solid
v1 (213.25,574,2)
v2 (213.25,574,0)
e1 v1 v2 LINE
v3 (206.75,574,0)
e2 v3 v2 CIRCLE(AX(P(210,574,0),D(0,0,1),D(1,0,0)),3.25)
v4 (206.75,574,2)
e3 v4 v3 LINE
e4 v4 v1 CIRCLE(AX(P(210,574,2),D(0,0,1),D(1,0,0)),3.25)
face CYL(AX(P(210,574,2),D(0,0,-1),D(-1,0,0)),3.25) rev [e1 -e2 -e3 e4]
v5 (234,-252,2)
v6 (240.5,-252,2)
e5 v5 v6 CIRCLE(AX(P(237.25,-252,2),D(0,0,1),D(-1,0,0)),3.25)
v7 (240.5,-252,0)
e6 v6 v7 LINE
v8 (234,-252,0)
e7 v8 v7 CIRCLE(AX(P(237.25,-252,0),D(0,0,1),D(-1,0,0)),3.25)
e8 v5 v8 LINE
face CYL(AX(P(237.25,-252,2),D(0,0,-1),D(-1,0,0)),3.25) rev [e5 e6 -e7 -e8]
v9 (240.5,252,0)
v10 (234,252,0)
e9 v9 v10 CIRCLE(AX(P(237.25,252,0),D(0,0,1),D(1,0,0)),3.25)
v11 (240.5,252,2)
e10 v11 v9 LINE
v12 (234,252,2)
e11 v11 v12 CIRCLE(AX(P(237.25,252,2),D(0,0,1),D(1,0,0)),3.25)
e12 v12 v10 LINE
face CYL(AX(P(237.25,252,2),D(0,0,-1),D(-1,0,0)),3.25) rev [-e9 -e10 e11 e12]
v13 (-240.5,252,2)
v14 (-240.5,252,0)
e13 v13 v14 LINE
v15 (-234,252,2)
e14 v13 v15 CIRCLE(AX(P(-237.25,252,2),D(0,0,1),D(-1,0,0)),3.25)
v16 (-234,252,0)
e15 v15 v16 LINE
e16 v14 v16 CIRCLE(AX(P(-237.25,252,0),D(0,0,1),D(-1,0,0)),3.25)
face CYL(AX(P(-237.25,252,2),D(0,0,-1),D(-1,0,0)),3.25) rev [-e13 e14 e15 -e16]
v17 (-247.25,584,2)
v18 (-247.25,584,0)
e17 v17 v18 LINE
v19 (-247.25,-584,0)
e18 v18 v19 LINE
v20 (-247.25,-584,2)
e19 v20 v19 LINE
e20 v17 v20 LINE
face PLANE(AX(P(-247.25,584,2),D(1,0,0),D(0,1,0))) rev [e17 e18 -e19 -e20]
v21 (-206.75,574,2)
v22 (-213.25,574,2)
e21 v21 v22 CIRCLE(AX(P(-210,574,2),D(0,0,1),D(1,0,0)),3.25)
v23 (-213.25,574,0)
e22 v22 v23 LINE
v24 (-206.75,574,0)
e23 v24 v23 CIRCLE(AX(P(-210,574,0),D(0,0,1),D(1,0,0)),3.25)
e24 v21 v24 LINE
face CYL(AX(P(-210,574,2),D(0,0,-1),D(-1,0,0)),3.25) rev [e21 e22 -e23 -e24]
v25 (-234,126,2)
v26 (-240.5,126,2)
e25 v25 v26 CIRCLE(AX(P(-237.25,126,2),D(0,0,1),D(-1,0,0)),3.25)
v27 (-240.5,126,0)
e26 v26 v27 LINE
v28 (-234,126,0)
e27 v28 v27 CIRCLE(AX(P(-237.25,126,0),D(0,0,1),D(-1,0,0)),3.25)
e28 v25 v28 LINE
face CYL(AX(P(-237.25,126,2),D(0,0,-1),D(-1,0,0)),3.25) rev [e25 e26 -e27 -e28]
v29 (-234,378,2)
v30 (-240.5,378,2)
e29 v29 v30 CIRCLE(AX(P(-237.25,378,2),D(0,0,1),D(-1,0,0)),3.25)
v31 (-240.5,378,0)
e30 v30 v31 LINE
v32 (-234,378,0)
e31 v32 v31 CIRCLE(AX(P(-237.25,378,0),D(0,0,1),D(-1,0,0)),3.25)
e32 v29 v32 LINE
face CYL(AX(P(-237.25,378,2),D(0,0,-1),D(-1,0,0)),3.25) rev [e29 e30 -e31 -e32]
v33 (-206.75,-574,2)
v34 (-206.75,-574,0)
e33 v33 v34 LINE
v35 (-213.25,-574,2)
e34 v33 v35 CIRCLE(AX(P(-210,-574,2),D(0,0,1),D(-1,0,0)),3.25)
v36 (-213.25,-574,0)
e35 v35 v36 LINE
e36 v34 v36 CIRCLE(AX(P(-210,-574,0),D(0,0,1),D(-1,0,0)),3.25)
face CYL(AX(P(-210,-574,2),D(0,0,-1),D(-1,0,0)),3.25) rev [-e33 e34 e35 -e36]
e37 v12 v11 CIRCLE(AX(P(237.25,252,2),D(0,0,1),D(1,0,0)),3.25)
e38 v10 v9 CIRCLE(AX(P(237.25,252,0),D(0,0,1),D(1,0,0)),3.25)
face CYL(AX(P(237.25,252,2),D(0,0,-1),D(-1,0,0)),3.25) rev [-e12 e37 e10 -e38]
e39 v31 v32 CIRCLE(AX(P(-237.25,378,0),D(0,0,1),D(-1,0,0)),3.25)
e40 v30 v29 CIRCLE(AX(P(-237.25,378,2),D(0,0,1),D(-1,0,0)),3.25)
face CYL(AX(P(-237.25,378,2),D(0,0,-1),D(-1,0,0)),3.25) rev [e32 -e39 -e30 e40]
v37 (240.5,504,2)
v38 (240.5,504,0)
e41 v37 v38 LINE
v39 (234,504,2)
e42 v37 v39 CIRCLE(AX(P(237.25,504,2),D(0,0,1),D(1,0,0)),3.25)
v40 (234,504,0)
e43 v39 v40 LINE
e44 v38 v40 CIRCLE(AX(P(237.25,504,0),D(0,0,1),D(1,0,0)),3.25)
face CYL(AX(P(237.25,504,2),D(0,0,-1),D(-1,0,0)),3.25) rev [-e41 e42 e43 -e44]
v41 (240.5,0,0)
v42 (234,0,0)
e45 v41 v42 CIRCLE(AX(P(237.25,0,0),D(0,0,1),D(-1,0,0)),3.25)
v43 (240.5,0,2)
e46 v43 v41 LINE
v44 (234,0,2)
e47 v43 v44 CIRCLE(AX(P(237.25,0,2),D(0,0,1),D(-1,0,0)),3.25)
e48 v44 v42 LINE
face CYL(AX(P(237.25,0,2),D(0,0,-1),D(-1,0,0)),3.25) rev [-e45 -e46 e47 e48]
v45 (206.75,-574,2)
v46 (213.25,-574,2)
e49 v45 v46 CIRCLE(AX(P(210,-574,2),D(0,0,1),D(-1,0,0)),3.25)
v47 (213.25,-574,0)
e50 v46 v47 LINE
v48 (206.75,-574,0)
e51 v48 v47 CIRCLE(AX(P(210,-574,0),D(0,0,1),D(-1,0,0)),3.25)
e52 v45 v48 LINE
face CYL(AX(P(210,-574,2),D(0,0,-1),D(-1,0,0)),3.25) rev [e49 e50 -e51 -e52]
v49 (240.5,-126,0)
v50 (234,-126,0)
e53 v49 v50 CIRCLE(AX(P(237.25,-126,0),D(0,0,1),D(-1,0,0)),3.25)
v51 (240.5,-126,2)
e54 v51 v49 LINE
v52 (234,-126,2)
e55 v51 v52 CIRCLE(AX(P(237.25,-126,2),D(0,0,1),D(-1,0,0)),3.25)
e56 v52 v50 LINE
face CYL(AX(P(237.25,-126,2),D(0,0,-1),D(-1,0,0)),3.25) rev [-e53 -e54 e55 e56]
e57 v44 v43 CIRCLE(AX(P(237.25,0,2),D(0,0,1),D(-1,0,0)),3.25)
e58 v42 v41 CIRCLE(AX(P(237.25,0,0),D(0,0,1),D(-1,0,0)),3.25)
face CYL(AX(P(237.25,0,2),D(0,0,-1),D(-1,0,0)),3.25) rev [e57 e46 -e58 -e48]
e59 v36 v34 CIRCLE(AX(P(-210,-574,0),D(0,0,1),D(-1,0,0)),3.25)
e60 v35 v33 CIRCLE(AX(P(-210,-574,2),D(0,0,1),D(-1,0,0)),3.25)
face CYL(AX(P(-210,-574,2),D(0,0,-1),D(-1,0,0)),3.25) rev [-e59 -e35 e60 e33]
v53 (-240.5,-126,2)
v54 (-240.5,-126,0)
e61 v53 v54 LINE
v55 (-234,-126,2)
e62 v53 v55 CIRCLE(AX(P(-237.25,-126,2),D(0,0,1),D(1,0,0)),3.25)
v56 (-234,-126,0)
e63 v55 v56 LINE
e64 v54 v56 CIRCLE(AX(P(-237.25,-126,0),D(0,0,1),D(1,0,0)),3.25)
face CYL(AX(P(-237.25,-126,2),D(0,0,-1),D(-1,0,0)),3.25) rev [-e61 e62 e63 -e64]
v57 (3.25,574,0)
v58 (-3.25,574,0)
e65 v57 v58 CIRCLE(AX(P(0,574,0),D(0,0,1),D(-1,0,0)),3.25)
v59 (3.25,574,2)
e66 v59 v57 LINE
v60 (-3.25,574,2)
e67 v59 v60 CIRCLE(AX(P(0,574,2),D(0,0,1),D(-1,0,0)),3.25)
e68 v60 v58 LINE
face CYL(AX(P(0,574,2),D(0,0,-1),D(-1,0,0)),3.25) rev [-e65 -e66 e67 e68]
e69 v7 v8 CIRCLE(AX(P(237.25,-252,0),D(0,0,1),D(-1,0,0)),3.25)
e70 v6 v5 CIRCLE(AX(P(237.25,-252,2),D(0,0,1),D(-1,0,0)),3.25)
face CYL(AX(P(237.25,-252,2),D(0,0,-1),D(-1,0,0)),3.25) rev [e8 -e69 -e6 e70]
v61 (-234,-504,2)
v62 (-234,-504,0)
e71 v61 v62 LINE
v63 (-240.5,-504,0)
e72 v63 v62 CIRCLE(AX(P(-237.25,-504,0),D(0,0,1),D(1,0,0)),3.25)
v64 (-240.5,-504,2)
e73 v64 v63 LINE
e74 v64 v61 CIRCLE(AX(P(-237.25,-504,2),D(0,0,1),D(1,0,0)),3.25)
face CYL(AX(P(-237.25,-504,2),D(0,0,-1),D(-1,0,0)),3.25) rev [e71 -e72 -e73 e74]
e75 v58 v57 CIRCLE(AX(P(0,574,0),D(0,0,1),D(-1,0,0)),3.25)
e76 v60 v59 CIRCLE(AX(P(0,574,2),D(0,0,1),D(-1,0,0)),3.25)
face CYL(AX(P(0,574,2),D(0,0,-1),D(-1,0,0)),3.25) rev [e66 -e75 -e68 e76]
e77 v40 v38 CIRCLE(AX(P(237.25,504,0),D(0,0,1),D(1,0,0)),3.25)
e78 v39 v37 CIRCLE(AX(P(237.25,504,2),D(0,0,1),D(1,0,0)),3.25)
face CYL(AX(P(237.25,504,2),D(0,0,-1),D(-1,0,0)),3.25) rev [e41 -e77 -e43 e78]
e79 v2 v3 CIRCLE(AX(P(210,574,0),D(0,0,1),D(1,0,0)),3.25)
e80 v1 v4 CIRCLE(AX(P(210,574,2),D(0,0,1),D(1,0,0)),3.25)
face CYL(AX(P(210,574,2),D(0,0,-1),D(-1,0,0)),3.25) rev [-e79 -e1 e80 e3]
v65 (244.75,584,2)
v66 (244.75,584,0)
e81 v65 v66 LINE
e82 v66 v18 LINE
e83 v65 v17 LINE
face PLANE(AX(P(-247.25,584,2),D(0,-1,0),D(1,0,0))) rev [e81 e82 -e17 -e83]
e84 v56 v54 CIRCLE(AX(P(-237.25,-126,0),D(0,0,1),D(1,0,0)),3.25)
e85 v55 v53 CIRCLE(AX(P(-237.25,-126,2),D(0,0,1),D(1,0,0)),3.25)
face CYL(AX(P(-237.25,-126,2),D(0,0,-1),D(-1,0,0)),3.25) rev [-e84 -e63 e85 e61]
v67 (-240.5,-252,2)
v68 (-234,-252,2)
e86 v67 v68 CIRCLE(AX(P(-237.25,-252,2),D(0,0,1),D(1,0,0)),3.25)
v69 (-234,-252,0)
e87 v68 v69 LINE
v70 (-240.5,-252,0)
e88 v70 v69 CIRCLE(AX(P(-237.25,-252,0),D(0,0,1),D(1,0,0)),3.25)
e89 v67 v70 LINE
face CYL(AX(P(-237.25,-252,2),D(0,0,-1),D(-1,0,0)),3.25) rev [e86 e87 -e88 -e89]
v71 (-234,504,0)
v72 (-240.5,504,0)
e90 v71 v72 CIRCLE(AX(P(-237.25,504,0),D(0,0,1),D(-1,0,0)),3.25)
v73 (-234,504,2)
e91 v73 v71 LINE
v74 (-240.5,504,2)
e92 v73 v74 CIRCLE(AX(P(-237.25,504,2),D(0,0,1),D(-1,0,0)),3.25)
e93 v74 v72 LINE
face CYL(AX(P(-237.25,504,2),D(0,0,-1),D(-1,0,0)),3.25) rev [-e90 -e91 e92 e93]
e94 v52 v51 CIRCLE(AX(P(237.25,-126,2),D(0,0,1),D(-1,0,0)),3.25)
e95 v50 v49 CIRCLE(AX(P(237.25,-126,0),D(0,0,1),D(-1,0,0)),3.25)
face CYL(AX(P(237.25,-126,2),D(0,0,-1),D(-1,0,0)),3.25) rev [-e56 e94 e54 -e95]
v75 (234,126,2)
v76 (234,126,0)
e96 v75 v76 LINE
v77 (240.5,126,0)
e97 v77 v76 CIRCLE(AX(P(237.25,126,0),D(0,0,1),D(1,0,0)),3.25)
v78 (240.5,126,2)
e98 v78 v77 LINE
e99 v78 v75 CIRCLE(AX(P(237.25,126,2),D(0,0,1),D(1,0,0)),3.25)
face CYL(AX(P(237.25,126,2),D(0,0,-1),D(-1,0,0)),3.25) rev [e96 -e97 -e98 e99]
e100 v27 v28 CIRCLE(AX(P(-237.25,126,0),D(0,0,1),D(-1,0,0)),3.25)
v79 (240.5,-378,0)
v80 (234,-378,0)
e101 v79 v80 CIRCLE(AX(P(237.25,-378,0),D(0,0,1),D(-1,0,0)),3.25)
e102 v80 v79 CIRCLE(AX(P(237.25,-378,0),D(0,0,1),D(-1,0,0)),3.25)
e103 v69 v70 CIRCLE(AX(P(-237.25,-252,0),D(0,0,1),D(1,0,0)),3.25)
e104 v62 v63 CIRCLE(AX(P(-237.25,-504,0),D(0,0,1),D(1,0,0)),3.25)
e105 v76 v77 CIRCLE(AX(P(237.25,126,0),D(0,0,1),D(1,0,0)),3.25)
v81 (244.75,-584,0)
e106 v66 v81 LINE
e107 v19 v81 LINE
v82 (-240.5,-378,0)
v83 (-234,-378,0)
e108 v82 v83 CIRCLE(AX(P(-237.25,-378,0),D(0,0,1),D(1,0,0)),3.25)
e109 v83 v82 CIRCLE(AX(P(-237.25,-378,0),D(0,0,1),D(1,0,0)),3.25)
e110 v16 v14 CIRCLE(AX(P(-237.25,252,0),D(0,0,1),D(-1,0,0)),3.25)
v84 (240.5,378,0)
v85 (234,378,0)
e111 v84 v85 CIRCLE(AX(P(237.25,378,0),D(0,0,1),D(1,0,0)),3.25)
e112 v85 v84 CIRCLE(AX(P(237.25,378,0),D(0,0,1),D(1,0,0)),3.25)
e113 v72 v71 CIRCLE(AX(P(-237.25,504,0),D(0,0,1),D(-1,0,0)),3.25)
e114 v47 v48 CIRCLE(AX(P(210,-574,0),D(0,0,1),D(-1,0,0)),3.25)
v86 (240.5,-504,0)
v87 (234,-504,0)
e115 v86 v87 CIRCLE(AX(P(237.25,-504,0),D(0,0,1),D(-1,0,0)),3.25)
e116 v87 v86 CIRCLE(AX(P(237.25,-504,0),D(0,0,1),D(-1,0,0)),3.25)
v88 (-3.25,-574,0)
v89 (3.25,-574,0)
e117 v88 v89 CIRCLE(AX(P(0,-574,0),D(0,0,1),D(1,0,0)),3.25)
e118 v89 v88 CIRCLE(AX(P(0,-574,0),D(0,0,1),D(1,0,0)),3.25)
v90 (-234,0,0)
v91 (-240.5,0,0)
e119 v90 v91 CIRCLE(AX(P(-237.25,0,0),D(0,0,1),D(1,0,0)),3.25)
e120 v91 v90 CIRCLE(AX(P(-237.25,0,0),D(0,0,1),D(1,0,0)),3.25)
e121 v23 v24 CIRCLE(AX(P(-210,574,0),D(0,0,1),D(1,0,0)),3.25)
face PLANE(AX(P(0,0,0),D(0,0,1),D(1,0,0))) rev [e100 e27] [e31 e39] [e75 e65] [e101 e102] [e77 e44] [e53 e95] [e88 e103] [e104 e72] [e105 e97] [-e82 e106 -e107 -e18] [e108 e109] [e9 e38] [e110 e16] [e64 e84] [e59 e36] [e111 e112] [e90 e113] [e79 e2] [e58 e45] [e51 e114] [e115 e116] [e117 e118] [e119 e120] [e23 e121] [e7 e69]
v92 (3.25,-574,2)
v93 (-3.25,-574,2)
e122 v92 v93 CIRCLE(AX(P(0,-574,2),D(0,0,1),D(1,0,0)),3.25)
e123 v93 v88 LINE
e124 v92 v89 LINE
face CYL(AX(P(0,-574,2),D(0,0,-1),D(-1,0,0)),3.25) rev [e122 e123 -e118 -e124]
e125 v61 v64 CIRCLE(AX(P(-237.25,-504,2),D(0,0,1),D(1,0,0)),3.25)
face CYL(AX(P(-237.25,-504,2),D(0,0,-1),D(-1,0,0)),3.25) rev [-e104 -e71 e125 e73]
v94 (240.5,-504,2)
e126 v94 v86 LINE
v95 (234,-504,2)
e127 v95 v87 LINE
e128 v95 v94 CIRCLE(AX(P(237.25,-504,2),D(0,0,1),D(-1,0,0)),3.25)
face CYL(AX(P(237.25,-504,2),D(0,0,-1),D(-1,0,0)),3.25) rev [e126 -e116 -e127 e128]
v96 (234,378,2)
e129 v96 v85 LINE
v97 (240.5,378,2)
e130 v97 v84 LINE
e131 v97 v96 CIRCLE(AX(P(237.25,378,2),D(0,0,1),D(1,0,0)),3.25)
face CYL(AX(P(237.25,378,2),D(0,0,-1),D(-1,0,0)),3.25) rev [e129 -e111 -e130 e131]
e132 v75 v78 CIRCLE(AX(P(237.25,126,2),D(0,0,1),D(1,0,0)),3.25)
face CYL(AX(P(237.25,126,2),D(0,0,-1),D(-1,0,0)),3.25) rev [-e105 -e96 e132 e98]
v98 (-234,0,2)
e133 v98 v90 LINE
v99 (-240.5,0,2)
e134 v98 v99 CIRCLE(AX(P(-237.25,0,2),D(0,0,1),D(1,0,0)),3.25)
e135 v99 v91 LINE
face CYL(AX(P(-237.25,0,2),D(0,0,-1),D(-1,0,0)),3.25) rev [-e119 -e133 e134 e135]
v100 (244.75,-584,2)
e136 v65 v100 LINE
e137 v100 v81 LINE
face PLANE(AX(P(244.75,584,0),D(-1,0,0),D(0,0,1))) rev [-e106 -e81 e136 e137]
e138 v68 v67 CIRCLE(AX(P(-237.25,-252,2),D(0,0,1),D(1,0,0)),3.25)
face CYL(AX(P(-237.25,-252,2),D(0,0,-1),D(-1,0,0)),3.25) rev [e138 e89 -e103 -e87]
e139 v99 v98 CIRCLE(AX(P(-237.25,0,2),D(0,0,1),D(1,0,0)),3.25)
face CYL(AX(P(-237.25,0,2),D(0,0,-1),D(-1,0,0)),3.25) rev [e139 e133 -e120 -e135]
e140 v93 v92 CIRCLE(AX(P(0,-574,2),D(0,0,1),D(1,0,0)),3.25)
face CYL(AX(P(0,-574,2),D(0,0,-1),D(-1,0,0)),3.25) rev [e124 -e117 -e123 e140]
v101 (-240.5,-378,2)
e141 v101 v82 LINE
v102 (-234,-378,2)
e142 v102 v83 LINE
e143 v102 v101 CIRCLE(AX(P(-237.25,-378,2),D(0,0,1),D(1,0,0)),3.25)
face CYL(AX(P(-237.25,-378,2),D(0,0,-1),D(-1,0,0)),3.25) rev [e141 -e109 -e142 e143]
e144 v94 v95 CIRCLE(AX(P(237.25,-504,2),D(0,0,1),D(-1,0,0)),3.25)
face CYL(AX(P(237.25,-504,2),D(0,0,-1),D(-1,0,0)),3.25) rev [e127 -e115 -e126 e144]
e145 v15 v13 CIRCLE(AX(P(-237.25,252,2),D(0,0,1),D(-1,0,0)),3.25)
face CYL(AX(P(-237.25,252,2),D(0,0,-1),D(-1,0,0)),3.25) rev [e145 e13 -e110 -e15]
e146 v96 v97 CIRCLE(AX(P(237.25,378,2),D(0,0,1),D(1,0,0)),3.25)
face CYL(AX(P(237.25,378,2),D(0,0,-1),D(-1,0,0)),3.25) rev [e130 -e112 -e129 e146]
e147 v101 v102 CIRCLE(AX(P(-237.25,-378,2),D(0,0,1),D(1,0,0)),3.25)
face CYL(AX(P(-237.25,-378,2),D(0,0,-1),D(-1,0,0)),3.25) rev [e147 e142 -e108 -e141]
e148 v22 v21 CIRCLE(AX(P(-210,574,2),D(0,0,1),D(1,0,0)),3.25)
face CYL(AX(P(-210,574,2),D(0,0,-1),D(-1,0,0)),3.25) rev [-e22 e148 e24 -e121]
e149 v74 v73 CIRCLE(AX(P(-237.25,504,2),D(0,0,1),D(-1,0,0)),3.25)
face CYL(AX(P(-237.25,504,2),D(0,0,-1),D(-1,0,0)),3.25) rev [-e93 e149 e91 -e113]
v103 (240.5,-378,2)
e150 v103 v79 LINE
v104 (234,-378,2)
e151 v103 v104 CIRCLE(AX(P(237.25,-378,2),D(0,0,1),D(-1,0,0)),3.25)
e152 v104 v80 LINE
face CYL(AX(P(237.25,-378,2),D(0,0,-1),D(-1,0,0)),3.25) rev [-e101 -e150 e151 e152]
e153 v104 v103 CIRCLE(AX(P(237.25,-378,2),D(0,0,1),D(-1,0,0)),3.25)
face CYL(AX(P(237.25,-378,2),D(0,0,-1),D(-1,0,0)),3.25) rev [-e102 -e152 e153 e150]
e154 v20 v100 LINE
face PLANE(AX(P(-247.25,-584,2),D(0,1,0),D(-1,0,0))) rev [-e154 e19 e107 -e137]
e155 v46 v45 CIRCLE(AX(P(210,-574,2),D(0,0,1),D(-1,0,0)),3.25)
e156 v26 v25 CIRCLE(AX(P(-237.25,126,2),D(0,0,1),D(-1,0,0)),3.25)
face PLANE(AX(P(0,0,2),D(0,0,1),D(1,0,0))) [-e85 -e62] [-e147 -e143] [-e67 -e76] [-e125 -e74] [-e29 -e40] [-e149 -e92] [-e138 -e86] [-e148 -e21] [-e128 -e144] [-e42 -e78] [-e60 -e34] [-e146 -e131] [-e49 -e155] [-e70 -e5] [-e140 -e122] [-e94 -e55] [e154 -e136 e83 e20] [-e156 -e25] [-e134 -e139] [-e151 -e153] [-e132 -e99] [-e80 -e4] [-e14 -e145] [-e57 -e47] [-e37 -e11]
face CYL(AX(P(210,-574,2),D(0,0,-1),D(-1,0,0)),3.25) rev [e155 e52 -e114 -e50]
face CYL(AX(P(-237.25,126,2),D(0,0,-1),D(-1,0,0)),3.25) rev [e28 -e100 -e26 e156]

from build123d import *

# Parameters (mm, degrees)
SKETCH_1_W          = 494.5
SKETCH_1_H          = 1168
SKETCH_1_R          = 3.25
EXTRUDE_1_DEPTH     = 2
SKETCH_2_W          = 2.5
SKETCH_2_H          = 2
CUT_EXTRUDE_1_DEPTH = 1194.884652092


with BuildPart() as part:
    # 草图1 → 凸台-拉伸1 (new body)
    with BuildSketch(Plane.XY):
        Rectangle(SKETCH_1_W, SKETCH_1_H)
        with Locations((-237.25, 0)):
            Circle(SKETCH_1_R, mode=Mode.SUBTRACT)
        with Locations((-237.25, -126)):
            Circle(SKETCH_1_R, mode=Mode.SUBTRACT)
        with Locations((-237.25, -252)):
            Circle(SKETCH_1_R, mode=Mode.SUBTRACT)
        with Locations((-237.25, -378)):
            Circle(SKETCH_1_R, mode=Mode.SUBTRACT)
        with Locations((-237.25, -504)):
            Circle(SKETCH_1_R, mode=Mode.SUBTRACT)
        with Locations((0, -574)):
            Circle(SKETCH_1_R, mode=Mode.SUBTRACT)
        with Locations(Location((0, 574, 0), (0, 0, 180))):
            Circle(SKETCH_1_R, mode=Mode.SUBTRACT)
        with Locations(Location((-237.25, 504, 0), (0, 0, 180))):
            Circle(SKETCH_1_R, mode=Mode.SUBTRACT)
        with Locations(Location((-237.25, 378, 0), (0, 0, 180))):
            Circle(SKETCH_1_R, mode=Mode.SUBTRACT)
        with Locations(Location((-237.25, 252, 0), (0, 0, 180))):
            Circle(SKETCH_1_R, mode=Mode.SUBTRACT)
        with Locations(Location((-237.25, 126, 0), (0, 0, 180))):
            Circle(SKETCH_1_R, mode=Mode.SUBTRACT)
        with Locations((237.25, 126)):
            Circle(SKETCH_1_R, mode=Mode.SUBTRACT)
        with Locations((237.25, 252)):
            Circle(SKETCH_1_R, mode=Mode.SUBTRACT)
        with Locations((237.25, 378)):
            Circle(SKETCH_1_R, mode=Mode.SUBTRACT)
        with Locations((237.25, 504)):
            Circle(SKETCH_1_R, mode=Mode.SUBTRACT)
        with Locations(Location((237.25, -504, 0), (0, 0, 180))):
            Circle(SKETCH_1_R, mode=Mode.SUBTRACT)
        with Locations(Location((237.25, -378, 0), (0, 0, 180))):
            Circle(SKETCH_1_R, mode=Mode.SUBTRACT)
        with Locations(Location((237.25, -252, 0), (0, 0, 180))):
            Circle(SKETCH_1_R, mode=Mode.SUBTRACT)
        with Locations(Location((237.25, -126, 0), (0, 0, 180))):
            Circle(SKETCH_1_R, mode=Mode.SUBTRACT)
        with Locations(Location((237.25, 0, 0), (0, 0, 180))):
            Circle(SKETCH_1_R, mode=Mode.SUBTRACT)
        with Locations((-210, 574)):
            Circle(SKETCH_1_R, mode=Mode.SUBTRACT)
        with Locations((210, 574)):
            Circle(SKETCH_1_R, mode=Mode.SUBTRACT)
        with Locations(Location((-210, -574, 0), (0, 0, 180))):
            Circle(SKETCH_1_R, mode=Mode.SUBTRACT)
        with Locations(Location((210, -574, 0), (0, 0, 180))):
            Circle(SKETCH_1_R, mode=Mode.SUBTRACT)
    extrude(amount=EXTRUDE_1_DEPTH)

    # 草图2 → 切除-拉伸1 (cut, through all)
    with BuildSketch(Plane.XZ.offset(584)):
        with Locations((246, 1)):
            Rectangle(SKETCH_2_W, SKETCH_2_H)
    extrude(amount=-CUT_EXTRUDE_1_DEPTH, mode=Mode.SUBTRACT)


solid = part.part
